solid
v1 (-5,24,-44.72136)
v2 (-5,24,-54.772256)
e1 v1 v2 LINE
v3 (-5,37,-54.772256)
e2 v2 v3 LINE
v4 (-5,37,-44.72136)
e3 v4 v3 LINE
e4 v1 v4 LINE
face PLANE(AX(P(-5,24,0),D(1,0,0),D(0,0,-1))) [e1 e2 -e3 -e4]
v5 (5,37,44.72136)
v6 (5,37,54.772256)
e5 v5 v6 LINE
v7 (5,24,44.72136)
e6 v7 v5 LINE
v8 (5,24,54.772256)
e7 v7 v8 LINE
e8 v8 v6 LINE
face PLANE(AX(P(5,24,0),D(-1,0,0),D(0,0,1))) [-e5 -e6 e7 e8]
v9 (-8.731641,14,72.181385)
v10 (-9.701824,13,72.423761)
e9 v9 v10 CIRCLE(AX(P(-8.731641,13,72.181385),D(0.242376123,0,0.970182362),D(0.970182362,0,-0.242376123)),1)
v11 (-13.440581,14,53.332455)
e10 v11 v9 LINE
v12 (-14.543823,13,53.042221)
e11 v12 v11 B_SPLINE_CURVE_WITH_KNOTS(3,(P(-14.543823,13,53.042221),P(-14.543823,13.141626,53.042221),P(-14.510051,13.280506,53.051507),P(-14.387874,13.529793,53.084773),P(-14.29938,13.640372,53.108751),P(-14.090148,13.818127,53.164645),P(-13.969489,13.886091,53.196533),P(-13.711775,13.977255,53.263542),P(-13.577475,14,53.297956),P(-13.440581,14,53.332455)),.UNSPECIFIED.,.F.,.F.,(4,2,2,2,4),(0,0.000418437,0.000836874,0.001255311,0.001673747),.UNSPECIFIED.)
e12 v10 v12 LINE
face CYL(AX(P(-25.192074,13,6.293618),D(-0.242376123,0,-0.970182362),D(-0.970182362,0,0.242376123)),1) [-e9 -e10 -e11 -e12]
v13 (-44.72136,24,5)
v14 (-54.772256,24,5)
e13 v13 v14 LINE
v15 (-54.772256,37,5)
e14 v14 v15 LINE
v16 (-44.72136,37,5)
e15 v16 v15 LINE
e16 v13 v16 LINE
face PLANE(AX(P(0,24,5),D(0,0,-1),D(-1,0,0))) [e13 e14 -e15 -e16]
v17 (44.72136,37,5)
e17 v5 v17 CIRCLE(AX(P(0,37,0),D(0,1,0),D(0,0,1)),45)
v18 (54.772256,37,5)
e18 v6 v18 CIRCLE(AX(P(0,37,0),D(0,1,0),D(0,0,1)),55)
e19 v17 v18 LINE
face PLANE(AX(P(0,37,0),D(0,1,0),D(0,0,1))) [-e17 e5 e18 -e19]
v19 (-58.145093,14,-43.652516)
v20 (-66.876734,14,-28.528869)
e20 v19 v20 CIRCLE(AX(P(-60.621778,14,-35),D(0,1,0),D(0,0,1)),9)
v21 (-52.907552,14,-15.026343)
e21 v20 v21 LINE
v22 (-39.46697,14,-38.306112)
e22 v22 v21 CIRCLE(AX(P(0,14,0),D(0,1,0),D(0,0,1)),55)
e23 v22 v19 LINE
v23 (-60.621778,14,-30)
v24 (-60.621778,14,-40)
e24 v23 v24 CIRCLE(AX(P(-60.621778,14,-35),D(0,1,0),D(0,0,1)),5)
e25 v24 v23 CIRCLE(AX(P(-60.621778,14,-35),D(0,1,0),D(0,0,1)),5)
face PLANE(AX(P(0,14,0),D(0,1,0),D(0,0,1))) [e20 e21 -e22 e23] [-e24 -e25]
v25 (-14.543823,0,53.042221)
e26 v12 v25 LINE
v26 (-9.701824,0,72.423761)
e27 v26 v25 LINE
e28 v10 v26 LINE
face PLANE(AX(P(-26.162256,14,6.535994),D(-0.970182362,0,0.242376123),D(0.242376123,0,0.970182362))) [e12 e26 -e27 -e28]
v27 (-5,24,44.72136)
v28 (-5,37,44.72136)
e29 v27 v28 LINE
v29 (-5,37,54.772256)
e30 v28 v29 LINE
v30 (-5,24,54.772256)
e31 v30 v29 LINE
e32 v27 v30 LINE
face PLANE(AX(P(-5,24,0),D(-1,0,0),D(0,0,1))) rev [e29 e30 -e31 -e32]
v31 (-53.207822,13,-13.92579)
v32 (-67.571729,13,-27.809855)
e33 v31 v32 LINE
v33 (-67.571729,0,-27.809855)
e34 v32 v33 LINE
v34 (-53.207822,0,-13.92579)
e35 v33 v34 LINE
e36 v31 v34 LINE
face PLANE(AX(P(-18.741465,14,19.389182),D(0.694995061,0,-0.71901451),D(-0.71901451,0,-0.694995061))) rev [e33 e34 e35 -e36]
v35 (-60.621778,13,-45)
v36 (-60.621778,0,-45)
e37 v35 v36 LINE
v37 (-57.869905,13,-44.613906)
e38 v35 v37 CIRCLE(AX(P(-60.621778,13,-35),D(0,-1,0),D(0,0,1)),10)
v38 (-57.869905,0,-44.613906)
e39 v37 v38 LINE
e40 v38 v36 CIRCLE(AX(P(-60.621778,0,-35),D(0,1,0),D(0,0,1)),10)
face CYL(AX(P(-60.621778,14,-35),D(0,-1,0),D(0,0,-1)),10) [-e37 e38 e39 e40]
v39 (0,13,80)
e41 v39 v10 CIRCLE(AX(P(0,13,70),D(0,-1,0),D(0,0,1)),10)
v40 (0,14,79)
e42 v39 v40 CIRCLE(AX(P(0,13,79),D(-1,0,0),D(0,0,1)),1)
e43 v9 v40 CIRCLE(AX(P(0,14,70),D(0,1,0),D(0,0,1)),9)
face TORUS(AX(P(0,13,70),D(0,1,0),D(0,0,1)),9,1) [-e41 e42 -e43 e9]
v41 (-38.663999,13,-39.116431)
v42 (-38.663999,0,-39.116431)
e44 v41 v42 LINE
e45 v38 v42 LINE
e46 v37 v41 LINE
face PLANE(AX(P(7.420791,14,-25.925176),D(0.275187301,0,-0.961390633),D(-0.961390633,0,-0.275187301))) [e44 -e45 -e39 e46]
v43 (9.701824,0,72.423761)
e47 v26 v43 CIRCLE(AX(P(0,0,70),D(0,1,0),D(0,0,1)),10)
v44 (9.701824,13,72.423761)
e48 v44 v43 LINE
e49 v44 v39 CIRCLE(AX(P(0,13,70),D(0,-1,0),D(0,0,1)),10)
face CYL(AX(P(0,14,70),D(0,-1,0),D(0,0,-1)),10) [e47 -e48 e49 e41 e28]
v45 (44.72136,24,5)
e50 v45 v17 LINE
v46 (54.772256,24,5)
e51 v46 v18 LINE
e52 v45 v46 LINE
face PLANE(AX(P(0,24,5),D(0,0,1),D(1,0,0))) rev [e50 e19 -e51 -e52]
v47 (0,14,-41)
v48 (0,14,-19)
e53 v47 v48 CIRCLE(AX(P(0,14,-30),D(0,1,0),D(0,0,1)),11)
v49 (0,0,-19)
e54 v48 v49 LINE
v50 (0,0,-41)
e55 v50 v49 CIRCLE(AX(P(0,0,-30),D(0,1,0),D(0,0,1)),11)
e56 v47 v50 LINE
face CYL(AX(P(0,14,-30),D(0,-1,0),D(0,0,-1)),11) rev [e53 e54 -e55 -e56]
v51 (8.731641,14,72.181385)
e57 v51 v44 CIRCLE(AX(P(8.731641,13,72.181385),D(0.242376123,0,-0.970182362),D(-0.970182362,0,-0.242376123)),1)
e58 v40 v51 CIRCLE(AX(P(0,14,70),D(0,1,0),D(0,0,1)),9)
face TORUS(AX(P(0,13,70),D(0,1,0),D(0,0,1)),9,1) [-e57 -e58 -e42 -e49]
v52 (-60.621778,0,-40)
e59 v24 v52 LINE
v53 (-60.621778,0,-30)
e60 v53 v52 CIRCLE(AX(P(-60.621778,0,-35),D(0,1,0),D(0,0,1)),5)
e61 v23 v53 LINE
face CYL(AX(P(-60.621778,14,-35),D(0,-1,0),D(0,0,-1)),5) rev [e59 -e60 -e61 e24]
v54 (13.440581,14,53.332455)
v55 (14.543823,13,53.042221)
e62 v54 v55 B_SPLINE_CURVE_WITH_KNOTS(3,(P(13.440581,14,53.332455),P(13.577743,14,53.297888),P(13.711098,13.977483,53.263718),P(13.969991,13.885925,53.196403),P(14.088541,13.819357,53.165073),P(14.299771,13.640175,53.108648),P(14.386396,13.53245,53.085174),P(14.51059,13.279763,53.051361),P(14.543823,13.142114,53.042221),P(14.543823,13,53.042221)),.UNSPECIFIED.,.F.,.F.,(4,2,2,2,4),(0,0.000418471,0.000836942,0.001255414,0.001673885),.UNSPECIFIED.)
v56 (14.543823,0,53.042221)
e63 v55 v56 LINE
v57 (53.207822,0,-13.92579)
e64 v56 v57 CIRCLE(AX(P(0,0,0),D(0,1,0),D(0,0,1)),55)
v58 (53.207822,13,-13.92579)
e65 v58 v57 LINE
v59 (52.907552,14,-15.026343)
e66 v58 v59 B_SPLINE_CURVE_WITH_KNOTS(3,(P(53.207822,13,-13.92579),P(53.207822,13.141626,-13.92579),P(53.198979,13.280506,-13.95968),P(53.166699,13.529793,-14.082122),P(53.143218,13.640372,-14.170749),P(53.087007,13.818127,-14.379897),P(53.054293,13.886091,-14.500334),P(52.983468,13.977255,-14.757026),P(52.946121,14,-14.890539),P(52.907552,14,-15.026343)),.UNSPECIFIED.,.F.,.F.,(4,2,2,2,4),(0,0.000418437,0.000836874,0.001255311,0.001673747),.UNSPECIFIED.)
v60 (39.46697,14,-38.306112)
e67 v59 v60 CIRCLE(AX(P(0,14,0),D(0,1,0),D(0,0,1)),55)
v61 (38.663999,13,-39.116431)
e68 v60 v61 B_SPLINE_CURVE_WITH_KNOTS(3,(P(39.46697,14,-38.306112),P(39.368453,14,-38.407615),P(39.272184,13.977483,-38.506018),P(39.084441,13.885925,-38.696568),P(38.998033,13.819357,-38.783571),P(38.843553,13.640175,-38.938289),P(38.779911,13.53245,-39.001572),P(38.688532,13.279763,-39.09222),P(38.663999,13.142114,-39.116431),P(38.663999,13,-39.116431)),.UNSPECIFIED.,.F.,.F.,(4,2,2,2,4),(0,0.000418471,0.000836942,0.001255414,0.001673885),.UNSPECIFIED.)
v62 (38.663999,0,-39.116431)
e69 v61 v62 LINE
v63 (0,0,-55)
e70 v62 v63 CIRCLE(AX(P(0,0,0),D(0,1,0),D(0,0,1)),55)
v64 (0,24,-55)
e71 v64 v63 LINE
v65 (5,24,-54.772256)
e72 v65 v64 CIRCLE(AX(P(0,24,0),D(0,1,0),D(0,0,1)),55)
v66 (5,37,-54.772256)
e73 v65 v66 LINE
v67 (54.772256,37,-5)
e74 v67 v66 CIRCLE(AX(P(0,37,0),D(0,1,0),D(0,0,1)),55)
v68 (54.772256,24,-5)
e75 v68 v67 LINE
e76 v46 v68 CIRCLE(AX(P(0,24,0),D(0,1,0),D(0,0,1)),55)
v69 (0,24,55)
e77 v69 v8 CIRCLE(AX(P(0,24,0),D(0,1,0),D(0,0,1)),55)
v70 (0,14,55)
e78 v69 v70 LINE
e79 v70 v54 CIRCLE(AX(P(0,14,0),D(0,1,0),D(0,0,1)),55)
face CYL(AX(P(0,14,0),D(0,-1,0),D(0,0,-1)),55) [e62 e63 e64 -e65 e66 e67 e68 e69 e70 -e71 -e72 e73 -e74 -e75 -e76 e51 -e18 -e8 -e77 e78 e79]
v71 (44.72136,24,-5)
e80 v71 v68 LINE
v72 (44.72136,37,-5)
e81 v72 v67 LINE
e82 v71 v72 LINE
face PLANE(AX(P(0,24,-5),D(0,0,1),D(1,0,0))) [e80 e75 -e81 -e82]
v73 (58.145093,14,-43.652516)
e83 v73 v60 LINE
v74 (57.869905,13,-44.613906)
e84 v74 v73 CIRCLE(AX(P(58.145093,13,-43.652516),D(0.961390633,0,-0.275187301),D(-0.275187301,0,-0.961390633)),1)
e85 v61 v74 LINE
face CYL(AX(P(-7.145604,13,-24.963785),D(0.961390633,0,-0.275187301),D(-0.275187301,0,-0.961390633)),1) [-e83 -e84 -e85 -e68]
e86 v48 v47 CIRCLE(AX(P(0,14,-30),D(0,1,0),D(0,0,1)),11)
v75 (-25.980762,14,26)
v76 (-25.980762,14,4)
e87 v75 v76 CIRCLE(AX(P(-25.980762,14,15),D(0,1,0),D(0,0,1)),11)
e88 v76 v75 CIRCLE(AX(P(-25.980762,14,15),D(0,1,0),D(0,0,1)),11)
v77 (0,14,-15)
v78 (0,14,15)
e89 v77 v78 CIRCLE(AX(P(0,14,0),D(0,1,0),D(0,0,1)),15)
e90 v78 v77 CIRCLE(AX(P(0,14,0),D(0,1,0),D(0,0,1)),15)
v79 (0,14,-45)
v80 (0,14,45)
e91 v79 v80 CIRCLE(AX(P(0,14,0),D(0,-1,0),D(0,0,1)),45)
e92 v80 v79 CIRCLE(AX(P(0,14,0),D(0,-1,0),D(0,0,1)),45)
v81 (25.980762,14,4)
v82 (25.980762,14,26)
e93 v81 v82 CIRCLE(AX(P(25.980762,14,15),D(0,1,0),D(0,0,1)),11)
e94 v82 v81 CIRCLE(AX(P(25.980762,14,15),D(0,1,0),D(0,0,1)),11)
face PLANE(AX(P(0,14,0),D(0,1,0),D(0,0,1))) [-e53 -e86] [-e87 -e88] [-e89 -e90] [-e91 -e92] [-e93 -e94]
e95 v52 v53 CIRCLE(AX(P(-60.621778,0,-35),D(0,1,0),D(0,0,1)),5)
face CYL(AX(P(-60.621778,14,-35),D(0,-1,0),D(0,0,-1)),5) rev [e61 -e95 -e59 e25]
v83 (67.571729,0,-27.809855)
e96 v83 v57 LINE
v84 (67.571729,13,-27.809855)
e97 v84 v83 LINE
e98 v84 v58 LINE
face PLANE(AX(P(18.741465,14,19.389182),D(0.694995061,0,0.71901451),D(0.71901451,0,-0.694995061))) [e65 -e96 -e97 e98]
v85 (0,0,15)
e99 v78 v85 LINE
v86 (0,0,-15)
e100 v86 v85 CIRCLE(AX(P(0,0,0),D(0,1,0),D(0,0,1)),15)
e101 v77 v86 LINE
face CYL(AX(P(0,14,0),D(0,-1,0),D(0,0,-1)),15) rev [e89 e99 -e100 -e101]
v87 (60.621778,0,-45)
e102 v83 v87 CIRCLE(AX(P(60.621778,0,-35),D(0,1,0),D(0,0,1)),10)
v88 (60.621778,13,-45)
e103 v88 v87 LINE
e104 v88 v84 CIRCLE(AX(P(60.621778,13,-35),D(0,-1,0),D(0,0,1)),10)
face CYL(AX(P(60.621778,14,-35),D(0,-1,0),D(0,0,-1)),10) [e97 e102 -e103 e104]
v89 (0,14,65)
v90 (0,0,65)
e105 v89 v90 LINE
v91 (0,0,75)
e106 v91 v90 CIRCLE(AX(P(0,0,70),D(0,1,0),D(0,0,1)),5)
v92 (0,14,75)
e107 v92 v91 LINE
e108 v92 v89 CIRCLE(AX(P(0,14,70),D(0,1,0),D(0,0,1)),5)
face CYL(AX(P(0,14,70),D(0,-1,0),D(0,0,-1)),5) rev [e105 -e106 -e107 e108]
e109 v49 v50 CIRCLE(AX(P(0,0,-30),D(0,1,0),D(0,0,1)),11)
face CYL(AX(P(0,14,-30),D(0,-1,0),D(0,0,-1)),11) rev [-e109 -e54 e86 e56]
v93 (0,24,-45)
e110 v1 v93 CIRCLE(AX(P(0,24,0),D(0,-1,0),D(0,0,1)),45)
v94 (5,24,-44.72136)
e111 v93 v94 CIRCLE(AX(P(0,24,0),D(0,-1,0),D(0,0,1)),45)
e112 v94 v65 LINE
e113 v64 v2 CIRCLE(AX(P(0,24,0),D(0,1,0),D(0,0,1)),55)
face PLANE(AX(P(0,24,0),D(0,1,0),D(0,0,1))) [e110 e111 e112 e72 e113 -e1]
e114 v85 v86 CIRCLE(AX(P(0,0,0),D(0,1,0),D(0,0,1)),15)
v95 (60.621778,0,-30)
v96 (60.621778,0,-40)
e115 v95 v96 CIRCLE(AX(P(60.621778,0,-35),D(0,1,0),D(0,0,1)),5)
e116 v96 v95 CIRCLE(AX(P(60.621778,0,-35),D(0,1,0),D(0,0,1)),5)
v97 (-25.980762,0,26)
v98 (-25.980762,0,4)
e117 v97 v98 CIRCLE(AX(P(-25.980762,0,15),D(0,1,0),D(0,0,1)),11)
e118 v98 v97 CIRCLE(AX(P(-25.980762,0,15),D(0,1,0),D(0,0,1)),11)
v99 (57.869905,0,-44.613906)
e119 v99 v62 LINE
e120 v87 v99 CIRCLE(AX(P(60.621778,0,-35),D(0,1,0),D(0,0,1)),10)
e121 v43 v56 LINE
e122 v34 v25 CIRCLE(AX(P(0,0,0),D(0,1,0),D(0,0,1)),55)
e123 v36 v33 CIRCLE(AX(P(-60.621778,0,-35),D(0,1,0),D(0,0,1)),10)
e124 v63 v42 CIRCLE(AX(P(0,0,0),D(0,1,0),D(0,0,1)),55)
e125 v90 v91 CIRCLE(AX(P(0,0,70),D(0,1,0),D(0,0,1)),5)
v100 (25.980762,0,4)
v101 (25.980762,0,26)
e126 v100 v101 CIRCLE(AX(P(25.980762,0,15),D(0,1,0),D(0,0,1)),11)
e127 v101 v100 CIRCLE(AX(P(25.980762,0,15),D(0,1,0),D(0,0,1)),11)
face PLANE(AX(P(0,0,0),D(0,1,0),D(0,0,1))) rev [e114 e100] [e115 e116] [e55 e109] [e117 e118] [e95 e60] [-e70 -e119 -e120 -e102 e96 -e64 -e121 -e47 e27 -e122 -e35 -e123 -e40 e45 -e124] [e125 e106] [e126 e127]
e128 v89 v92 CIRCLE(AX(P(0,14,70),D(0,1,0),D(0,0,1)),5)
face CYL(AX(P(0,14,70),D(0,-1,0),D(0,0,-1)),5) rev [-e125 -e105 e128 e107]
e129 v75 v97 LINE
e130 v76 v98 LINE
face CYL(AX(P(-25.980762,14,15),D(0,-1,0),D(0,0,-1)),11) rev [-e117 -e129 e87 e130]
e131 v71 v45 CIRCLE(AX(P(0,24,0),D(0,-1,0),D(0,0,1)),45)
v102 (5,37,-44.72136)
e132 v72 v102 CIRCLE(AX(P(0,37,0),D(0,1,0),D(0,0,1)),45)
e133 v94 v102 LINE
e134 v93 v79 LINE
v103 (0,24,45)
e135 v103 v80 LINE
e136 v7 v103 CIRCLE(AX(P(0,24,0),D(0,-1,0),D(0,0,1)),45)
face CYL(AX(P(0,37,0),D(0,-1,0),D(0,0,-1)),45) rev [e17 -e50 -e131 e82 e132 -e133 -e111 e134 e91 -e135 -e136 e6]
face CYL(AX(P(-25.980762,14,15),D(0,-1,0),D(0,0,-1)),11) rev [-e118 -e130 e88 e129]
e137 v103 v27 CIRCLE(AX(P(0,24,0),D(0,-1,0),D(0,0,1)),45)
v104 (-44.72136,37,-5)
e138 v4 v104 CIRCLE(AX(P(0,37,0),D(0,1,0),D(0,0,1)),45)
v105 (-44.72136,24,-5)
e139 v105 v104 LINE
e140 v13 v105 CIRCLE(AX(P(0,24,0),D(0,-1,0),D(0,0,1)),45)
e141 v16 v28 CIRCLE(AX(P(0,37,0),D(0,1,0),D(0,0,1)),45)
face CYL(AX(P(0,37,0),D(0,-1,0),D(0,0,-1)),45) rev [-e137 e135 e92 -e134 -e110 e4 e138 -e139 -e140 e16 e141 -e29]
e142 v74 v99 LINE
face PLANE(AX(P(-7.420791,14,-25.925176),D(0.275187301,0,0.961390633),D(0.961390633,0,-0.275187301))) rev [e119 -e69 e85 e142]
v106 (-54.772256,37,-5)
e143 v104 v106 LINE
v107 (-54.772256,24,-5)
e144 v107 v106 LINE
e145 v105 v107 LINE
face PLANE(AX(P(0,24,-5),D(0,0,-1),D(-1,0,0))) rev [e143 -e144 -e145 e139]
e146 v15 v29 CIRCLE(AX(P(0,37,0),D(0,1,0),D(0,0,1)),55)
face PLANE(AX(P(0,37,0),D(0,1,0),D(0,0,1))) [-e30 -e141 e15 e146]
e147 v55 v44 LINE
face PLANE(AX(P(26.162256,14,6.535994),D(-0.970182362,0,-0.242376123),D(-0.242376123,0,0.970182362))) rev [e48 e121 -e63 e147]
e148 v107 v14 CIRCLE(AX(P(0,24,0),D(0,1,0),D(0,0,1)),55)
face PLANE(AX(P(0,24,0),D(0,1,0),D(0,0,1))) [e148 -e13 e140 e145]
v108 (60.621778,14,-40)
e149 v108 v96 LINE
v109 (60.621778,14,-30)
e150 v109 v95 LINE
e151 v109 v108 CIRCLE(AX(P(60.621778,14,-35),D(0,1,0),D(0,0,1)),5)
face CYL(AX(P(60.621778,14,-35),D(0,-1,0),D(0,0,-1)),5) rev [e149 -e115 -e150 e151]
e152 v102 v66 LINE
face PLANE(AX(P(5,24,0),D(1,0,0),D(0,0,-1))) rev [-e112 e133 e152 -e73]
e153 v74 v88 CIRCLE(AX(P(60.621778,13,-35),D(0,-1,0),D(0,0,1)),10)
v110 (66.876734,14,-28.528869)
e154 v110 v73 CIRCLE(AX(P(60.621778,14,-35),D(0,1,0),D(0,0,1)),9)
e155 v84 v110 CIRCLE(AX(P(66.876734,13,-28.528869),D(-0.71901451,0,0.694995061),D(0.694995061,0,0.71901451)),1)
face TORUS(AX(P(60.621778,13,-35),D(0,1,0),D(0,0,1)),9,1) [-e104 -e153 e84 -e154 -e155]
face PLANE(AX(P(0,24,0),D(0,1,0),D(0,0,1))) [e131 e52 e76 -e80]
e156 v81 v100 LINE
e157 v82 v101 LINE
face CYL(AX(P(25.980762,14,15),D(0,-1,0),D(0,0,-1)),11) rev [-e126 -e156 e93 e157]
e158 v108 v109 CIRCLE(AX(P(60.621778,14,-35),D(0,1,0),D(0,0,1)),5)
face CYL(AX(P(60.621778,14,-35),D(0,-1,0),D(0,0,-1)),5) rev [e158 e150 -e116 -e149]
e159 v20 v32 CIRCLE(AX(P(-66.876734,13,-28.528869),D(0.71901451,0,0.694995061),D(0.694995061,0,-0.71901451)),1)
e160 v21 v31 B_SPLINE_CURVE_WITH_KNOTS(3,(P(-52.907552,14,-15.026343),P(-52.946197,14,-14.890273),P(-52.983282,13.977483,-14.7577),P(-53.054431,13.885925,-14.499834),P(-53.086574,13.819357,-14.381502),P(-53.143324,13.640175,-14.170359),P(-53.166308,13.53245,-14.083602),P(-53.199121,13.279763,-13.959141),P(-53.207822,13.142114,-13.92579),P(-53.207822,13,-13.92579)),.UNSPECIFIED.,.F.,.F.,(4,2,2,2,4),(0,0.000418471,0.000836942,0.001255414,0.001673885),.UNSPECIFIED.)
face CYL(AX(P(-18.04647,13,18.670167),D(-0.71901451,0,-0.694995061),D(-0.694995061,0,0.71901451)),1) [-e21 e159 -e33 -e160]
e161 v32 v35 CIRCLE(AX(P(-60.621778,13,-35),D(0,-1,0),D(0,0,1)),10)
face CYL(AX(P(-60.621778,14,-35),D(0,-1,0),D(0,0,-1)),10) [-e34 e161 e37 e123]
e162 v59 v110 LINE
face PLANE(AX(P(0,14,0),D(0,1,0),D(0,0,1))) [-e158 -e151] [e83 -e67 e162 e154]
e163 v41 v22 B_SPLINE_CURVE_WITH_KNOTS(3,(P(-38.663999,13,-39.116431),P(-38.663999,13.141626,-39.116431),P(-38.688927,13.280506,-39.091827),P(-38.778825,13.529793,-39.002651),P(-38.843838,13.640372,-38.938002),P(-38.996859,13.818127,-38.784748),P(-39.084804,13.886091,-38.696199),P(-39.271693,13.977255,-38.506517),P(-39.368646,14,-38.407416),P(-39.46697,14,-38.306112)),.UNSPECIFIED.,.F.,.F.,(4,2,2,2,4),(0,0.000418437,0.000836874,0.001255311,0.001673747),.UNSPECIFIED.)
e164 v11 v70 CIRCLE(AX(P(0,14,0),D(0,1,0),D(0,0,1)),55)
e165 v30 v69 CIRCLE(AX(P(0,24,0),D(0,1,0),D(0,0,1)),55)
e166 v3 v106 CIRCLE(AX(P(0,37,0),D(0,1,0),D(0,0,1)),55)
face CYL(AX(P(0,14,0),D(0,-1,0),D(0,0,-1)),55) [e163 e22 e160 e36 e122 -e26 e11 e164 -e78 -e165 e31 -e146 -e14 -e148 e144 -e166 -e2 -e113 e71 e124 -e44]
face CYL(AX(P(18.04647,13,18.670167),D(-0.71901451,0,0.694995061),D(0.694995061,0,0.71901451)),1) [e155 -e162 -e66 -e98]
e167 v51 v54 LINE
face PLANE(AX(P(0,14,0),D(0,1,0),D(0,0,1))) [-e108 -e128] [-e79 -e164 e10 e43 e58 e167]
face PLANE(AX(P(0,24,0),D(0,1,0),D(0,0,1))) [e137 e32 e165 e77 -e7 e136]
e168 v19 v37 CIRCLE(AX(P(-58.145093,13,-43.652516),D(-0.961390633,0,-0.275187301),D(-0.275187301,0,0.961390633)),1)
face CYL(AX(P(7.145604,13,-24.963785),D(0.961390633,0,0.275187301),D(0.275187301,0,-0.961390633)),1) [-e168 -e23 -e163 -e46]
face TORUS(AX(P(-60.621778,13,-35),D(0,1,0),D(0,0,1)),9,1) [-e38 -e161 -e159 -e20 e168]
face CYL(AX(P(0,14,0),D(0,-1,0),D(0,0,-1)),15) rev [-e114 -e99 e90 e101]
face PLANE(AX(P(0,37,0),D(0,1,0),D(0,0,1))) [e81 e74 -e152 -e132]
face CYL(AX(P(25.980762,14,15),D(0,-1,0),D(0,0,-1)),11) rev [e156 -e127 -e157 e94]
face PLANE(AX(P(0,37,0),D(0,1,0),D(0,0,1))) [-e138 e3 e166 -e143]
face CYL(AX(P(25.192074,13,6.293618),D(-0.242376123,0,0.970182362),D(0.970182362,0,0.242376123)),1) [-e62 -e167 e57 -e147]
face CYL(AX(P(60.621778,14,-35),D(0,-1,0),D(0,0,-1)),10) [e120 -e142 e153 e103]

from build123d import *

# Parameters (mm, degrees)
FLANGE_PROFILE_SKETCH_R      = 45
FLANGE_PROFILE_SKETCH_R_2    = 5
FLANGE_PROFILE_SKETCH_R_3    = 15
FLANGE_PROFILE_SKETCH_R_4    = 11
MOUNTING_FLANGE_3_LUGS_DEPTH = 14
FLANGE_EDGE_FILLET_R1_R      = 1
BEARING_WALL_SKETCH_R        = 55
BEARING_WALL_SKETCH_R_2      = 45
BEARING_WALL_110_DEPTH       = 23
WALL_START                   = -13
WALL_SLOTS_4X_DEPTH          = 13


with BuildPart() as part:
    # Flange Profile Sketch → Mounting Flange 3 Lugs (new body)
    # profile 1 of 2: a face of its own
    with BuildSketch(Plane(origin=(0, 0, 0), x_dir=(1, 0, 0), z_dir=(0, 1, 0))):
        with BuildLine():
            Line((9.701823617, -72.423761231), (14.543823193, -53.042220984))
            ThreePointArc((14.543823193, -53.042220984), (47.631397208, -27.5), (53.207822442, 13.925790139))
            Line((53.207822442, 13.925790139), (67.571728872, 27.8098549))
            ThreePointArc((67.571728872, 27.8098549), (69.282032303, 40), (57.869905255, 44.613906331))
            Line((57.869905255, 44.613906331), (38.663999249, 39.116430845))
            ThreePointArc((38.663999249, 39.116430845), (0, 55), (-38.663999249, 39.116430845))
            Line((-38.663999249, 39.116430845), (-57.869905255, 44.613906331))
            ThreePointArc((-57.869905255, 44.613906331), (-69.282032303, 40), (-67.571728872, 27.8098549))
            Line((-67.571728872, 27.8098549), (-53.207822442, 13.925790139))
            ThreePointArc((-53.207822442, 13.925790139), (-47.631397208, -27.5), (-14.543823193, -53.042220984))
            Line((-14.543823193, -53.042220984), (-9.701823617, -72.423761231))
            ThreePointArc((-9.701823617, -72.423761231), (0, -80), (9.701823617, -72.423761231))
        make_face()
        Circle(FLANGE_PROFILE_SKETCH_R, mode=Mode.SUBTRACT)
        with Locations(Location((0, -70, 0), (0, 0, 270))):
            Circle(FLANGE_PROFILE_SKETCH_R_2, mode=Mode.SUBTRACT)
        with Locations(Location((-60.621778265, 35, 0), (0, 0, 270))):
            Circle(FLANGE_PROFILE_SKETCH_R_2, mode=Mode.SUBTRACT)
        with Locations(Location((60.621778265, 35, 0), (0, 0, 270))):
            Circle(FLANGE_PROFILE_SKETCH_R_2, mode=Mode.SUBTRACT)
    # profile 2 of 2: a face of its own
    with BuildSketch(Plane(origin=(0, 0, 0), x_dir=(1, 0, 0), z_dir=(0, 1, 0))):
        Circle(FLANGE_PROFILE_SKETCH_R)
        with Locations(Location((0, 0, 0), (0, 0, 270))):
            Circle(FLANGE_PROFILE_SKETCH_R_3, mode=Mode.SUBTRACT)
        with Locations(Location((-25.980762114, -15, 0), (0, 0, 270))):
            Circle(FLANGE_PROFILE_SKETCH_R_4, mode=Mode.SUBTRACT)
        with Locations(Location((25.980762114, -15, 0), (0, 0, 270))):
            Circle(FLANGE_PROFILE_SKETCH_R_4, mode=Mode.SUBTRACT)
        with Locations(Location((0, 30, 0), (0, 0, 270))):
            Circle(FLANGE_PROFILE_SKETCH_R_4, mode=Mode.SUBTRACT)
    extrude(amount=MOUNTING_FLANGE_3_LUGS_DEPTH)

    # Flange Edge Fillet R1
    flange_edge_fillet_r1_edges = [part.edges().sort_by_distance(p)[0] for p in [
        (12.122823405, 14, 62.732991107),
        (60.389775657, 14, -20.867822519),
        (69.282032303, 14, -40),
        (48.266952252, 14, -41.865168588),
        (-48.266952252, 14, -41.865168588),
        (-69.282032303, 14, -40),
        (-60.389775657, 14, -20.867822519),
        (-12.122823405, 14, 62.732991107),
        (0, 14, 80),
    ]]
    fillet(flange_edge_fillet_r1_edges, radius=FLANGE_EDGE_FILLET_R1_R)

    # Bearing Wall Sketch → Bearing Wall Ø110 (add)
    with BuildSketch(Plane(origin=(0, 14, 0), x_dir=(1, 0, 0), z_dir=(0, 1, 0))):
        with Locations(Location((0, 0, 0), (0, 0, 134.666726854))):
            Circle(BEARING_WALL_SKETCH_R)
        with Locations(Location((0, 0, 0), (0, 0, 270))):
            Circle(BEARING_WALL_SKETCH_R_2, mode=Mode.SUBTRACT)
    extrude(amount=BEARING_WALL_110_DEPTH)

    # Wall Slots Sketch → Wall Slots 4x (cut)
    with BuildSketch(Plane(origin=(0, 37, 0), x_dir=(1, 0, 0), z_dir=(0, 1, 0)).offset(WALL_START)):
        with BuildLine():
            ThreePointArc((-44.72135955, -5), (-45, 0), (-44.72135955, 5))
            Line((-44.72135955, 5), (-54.772255751, 5))
            ThreePointArc((-54.772255751, 5), (-55, 0), (-54.772255751, -5))
            Line((-54.772255751, -5), (-44.72135955, -5))
        make_face()
        with BuildLine():
            Line((-5, 54.772255751), (-5, 44.72135955))
            ThreePointArc((-5, 44.72135955), (0, 45), (5, 44.72135955))
            Line((5, 44.72135955), (5, 54.772255751))
            ThreePointArc((5, 54.772255751), (0, 55), (-5, 54.772255751))
        make_face()
        with BuildLine():
            Line((54.772255751, 5), (44.72135955, 5))
            ThreePointArc((44.72135955, 5), (44.930285887, 2.503879016), (45, 0))
            ThreePointArc((45, 0), (44.930285887, -2.503879016), (44.72135955, -5))
            Line((44.72135955, -5), (54.772255751, -5))
            ThreePointArc((54.772255751, -5), (54.943034437, -2.502592028), (55, 0))
            ThreePointArc((55, 0), (54.943034437, 2.502592028), (54.772255751, 5))
        make_face()
        with BuildLine():
            ThreePointArc((5, -44.72135955), (0, -45), (-5, -44.72135955))
            Line((-5, -44.72135955), (-5, -54.772255751))
            ThreePointArc((-5, -54.772255751), (0, -55), (5, -54.772255751))
            Line((5, -54.772255751), (5, -44.72135955))
        make_face()
    extrude(amount=WALL_SLOTS_4X_DEPTH, mode=Mode.SUBTRACT)


solid = part.part
